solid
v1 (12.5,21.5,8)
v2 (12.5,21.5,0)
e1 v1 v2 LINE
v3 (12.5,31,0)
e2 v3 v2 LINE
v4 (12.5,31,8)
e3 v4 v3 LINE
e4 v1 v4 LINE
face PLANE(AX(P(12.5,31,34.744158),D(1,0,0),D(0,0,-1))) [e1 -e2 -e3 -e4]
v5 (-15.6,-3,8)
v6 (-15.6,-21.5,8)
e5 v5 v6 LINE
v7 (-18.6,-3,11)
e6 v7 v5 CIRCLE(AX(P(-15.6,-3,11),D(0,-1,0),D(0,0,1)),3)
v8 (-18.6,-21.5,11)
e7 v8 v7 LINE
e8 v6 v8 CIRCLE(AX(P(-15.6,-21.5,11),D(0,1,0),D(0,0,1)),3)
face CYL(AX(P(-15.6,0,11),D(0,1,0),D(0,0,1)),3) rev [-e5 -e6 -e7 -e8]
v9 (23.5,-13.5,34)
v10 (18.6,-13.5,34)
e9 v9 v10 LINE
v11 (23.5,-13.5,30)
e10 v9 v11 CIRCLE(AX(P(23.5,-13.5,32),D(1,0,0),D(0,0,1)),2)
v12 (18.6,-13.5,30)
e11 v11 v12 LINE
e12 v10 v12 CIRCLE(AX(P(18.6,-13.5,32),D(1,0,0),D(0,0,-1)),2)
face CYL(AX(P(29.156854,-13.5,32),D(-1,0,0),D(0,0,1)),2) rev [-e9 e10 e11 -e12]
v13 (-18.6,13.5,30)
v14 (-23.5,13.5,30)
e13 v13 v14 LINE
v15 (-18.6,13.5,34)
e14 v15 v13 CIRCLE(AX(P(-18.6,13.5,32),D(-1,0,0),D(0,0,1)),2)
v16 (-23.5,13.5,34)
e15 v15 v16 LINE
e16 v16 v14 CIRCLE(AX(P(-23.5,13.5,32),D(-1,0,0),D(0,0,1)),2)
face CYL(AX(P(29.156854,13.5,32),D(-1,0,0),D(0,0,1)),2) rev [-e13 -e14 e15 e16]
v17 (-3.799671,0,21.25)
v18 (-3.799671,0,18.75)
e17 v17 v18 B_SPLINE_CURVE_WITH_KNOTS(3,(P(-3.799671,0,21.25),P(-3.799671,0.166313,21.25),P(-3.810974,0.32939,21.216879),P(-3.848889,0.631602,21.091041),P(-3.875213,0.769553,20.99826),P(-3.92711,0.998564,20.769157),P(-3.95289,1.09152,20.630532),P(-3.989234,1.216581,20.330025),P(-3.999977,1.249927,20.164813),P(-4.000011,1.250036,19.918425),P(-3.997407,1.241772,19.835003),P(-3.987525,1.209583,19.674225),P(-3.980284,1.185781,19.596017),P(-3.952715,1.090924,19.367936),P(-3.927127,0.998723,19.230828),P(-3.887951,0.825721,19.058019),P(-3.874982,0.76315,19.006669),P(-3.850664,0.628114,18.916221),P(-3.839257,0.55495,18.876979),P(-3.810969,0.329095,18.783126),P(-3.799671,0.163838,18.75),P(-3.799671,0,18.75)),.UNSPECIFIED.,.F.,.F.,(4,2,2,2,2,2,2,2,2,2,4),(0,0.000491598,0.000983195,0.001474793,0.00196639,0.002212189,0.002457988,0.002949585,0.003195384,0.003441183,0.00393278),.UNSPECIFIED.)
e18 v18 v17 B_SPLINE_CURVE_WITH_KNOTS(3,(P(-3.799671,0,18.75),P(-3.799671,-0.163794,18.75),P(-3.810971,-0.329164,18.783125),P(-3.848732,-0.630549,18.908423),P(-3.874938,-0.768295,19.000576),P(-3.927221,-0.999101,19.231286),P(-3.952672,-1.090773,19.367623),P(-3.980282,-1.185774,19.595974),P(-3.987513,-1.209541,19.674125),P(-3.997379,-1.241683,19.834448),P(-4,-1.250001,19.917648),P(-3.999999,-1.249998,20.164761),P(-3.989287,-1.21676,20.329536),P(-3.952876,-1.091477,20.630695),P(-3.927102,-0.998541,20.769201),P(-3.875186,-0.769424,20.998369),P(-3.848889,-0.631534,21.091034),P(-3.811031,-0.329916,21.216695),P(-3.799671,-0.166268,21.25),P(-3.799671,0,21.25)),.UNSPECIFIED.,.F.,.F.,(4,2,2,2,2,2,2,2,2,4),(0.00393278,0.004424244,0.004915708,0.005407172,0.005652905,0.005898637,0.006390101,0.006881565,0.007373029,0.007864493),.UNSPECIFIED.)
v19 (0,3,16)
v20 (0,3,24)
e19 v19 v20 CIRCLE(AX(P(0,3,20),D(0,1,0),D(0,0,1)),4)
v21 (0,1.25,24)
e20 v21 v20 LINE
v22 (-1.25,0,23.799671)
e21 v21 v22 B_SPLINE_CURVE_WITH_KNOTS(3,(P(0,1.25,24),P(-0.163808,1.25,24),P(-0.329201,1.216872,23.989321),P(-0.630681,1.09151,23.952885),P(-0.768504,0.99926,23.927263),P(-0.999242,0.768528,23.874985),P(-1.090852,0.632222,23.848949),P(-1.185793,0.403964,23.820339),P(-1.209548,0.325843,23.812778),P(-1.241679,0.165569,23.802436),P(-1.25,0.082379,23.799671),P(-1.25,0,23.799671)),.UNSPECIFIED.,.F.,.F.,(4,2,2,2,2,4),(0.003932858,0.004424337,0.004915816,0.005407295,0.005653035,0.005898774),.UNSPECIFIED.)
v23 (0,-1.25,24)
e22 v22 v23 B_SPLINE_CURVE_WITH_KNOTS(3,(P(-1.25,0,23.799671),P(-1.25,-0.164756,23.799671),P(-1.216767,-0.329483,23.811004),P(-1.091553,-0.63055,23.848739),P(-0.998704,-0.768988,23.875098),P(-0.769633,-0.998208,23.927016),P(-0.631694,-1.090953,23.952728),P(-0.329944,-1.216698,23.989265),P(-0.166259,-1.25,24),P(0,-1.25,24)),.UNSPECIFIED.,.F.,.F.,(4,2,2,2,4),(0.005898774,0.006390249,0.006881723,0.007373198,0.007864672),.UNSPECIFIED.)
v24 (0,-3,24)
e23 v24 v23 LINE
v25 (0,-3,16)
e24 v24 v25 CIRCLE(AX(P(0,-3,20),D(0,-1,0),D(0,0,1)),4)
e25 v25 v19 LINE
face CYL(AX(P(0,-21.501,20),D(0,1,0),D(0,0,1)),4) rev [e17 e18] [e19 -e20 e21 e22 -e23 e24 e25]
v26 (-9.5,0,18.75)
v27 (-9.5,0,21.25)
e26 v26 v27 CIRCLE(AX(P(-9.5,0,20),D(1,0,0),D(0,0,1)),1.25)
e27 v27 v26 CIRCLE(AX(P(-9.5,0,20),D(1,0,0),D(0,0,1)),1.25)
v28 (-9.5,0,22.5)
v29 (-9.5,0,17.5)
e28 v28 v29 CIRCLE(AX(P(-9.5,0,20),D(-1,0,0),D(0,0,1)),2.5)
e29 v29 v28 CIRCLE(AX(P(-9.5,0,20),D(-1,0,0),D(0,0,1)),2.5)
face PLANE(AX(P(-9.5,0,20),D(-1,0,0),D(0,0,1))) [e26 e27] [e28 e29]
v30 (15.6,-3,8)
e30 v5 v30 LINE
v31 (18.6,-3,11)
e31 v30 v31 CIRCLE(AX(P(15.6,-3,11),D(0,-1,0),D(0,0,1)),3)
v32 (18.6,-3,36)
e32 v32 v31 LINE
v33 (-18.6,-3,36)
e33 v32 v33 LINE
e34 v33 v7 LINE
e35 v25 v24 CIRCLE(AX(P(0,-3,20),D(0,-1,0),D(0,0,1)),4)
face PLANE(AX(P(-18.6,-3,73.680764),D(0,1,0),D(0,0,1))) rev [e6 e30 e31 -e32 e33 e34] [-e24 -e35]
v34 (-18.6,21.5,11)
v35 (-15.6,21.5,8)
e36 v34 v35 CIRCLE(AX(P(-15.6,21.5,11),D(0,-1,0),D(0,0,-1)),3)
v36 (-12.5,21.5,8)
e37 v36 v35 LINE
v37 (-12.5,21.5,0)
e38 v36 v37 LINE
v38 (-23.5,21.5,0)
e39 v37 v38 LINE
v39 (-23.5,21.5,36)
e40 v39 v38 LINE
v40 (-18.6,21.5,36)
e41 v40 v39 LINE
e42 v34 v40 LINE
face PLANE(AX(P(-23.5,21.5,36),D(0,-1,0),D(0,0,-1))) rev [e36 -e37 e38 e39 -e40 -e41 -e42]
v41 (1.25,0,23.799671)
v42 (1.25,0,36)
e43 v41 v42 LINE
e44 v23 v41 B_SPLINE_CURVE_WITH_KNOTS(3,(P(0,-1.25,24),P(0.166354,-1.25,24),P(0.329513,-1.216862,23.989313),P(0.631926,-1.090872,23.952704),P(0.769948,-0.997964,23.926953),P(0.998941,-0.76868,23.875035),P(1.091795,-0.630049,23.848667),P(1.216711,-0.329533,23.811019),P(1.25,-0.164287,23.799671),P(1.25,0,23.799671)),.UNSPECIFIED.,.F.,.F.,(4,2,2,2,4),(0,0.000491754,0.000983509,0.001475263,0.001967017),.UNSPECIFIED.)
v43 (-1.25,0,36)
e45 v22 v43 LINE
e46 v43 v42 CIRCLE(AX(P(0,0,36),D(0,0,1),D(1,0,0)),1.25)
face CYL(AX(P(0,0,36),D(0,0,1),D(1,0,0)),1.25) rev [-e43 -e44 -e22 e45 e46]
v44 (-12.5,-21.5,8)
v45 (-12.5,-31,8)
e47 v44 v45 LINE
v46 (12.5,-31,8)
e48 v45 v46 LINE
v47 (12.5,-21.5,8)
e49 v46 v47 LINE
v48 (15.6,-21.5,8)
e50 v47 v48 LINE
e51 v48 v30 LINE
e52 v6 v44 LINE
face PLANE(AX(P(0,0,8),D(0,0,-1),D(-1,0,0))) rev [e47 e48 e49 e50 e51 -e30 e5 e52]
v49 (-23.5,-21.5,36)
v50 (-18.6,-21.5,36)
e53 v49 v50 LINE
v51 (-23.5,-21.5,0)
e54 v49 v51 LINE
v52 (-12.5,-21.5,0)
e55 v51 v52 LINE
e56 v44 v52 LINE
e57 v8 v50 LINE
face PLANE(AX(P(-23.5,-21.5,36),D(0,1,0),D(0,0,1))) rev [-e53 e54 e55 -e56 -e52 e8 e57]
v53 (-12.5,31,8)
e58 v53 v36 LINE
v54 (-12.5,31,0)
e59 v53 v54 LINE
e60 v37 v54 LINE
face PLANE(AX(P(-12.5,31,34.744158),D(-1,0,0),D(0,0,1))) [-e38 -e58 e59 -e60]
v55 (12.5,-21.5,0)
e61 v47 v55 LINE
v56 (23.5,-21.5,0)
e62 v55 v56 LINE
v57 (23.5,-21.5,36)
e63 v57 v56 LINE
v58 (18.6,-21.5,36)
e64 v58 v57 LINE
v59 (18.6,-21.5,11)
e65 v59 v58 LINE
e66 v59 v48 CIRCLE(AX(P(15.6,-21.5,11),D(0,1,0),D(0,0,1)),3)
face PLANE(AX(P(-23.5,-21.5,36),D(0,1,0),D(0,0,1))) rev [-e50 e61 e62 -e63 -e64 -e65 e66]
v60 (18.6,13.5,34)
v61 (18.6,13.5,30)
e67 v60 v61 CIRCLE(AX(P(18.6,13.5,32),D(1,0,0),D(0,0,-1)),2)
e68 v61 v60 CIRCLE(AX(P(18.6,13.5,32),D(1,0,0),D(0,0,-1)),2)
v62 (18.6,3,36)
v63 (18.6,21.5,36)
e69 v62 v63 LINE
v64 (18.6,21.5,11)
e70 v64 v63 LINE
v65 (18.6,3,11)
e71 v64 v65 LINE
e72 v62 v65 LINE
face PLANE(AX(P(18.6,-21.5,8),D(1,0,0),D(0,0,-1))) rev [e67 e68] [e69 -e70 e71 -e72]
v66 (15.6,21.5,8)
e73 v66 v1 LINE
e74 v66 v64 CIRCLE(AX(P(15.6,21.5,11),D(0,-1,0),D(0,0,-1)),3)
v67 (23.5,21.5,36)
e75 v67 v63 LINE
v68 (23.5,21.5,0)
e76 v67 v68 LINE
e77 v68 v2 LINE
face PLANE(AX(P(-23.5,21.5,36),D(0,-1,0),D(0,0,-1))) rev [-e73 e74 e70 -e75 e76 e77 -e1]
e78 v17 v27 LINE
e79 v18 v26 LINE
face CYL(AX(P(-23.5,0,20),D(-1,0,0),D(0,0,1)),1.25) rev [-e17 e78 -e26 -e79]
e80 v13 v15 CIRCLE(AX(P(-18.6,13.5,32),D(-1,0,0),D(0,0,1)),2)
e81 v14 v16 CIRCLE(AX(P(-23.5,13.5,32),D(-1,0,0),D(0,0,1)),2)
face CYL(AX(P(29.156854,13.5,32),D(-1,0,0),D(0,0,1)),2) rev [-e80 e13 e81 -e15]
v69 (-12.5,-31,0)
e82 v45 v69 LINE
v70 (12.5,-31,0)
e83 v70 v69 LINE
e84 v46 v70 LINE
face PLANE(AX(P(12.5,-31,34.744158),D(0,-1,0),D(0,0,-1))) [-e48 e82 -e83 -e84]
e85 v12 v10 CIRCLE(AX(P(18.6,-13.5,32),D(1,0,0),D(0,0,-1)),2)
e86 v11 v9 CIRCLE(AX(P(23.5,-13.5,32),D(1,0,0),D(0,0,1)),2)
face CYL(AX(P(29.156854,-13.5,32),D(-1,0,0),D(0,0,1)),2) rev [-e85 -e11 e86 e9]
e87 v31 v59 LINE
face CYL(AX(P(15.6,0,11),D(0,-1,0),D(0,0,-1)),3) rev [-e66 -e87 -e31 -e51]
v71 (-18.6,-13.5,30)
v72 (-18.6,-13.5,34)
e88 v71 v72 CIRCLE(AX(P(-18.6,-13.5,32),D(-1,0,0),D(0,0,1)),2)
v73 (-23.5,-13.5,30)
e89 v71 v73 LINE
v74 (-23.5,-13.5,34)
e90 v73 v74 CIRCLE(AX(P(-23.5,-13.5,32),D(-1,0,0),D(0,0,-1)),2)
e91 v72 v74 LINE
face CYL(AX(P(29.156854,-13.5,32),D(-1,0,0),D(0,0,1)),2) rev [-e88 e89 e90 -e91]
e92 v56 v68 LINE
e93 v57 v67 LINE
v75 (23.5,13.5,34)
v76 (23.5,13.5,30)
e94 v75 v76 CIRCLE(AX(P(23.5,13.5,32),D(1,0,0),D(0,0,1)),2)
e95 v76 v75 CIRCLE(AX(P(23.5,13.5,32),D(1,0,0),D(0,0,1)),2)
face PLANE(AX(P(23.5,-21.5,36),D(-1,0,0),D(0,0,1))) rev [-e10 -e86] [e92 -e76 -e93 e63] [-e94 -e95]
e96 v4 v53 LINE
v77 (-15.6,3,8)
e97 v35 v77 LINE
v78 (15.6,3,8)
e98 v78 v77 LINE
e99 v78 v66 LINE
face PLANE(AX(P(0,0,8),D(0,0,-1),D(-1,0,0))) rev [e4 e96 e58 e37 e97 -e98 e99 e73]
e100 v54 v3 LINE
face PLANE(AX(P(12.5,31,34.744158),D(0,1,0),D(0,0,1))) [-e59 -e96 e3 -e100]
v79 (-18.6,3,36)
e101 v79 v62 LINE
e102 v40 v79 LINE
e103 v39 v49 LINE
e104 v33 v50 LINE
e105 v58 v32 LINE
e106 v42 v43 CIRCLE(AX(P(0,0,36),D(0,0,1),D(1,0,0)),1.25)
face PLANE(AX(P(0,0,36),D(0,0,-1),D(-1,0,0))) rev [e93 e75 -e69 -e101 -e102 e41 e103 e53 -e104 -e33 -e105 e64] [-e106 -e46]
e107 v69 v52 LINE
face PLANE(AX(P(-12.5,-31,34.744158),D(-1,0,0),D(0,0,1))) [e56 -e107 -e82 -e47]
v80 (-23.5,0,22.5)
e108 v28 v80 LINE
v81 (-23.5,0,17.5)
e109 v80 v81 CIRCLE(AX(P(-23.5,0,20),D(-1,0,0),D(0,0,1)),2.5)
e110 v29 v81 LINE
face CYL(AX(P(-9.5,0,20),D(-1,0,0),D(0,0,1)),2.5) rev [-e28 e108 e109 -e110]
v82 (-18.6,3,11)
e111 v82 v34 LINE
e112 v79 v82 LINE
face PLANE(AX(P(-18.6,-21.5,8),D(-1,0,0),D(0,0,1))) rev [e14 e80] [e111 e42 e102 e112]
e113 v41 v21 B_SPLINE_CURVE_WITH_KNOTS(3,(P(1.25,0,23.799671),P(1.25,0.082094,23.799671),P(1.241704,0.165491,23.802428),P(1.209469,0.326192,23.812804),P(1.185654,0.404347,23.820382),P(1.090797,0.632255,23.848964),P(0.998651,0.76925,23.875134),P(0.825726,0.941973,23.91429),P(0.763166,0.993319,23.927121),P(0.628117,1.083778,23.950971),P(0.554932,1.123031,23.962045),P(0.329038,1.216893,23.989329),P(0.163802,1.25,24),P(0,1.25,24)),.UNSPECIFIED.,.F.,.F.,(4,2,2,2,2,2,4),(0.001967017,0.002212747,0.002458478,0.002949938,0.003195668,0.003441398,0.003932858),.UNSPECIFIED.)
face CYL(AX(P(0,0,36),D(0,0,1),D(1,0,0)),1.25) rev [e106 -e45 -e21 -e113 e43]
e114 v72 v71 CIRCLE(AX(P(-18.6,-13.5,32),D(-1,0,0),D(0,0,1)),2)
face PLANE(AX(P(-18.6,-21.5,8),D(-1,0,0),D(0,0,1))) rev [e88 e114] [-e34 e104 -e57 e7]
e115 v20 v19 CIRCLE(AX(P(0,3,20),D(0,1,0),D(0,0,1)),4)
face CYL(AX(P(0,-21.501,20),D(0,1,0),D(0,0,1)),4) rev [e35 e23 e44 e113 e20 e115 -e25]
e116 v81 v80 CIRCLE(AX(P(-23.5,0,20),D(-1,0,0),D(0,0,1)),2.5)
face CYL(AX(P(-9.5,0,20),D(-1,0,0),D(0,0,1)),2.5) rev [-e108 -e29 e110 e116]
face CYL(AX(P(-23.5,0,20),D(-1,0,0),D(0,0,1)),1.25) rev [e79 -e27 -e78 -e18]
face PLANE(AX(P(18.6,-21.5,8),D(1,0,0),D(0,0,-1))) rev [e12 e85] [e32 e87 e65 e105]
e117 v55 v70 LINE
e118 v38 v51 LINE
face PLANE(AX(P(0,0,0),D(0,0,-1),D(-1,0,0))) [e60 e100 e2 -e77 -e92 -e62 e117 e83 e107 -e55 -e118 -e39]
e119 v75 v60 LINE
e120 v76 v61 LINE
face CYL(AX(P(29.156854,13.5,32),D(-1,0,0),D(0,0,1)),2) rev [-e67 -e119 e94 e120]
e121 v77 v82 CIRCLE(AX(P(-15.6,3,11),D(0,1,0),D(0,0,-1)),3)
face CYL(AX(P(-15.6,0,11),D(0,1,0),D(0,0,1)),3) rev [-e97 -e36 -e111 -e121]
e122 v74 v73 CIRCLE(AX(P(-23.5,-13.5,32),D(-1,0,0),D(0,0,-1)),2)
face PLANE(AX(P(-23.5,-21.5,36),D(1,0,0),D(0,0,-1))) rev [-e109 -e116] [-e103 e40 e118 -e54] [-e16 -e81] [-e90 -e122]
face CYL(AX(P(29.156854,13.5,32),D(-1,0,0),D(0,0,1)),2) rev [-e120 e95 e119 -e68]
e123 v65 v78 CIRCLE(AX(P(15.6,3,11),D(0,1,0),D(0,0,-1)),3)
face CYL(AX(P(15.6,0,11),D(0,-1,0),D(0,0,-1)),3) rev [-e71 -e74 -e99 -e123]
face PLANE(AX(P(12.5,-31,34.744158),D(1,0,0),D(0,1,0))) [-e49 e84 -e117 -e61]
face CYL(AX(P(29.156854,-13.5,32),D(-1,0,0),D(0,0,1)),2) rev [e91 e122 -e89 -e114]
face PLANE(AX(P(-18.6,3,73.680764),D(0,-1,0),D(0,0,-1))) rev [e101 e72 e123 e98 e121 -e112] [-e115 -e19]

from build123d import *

# Parameters (mm, degrees)
SKETCH_1_W              = 47
SKETCH_1_H              = 43
EXTRUDE_1_DEPTH         = 36
SKETCH_2_W              = 37.2
SKETCH_2_H              = 43
CUT_EXTRUDE_1_DEPTH     = 28
CUT_EXTRUDE_2_REACH     = 64.986
SKETCH_3_R              = 2
SKETCH_4_W              = 37.2
SKETCH_4_H              = 6
EXTRUDE_2_DEPTH         = 28
FILLET_1_R              = 3
CUT_EXTRUDE_3_REACH     = 51.482
SKETCH_5_R              = 4
HOLE_WIZARD_M3_1_REACH  = 50.068
HOLE_WIZARD_M3_1_BORE_R = 1.25
HOLE_WIZARD_M3_2_REACH  = 57.419
HOLE_WIZARD_M3_2_BORE_R = 1.25
SKETCH_8_W              = 25
SKETCH_8_H              = 9.5
EXTRUDE_3_DEPTH         = 8
SKETCH_9_R              = 2.5
CUT_EXTRUDE_4_DEPTH     = 14


with BuildPart() as part:
    # 草图1 → 凸台-拉伸1 (new body)
    with BuildSketch(Plane.XY):
        Rectangle(SKETCH_1_W, SKETCH_1_H)
    extrude(amount=EXTRUDE_1_DEPTH)

    # 草图2 → 切除-拉伸1 (cut)
    with BuildSketch(Plane.XY.offset(36)):
        Rectangle(SKETCH_2_W, SKETCH_2_H)
    extrude(amount=-CUT_EXTRUDE_1_DEPTH, mode=Mode.SUBTRACT)

    # 切除-拉伸2: up to this face of the body (flat: up to its plane)
    cut_extrude_2_end = Plane(part.part.faces().sort_by_distance((23.5, 0, 18))[0])
    # 草图3 → 切除-拉伸2 (cut, up to the picked face)
    with BuildSketch(Plane.ZY.offset(23.5), mode=Mode.PRIVATE) as cut_extrude_2_sk1:
        with Locations((32, 13.5)):
            Circle(SKETCH_3_R)
    cut_extrude_2_tool1 = split(extrude(cut_extrude_2_sk1.sketch, amount=-CUT_EXTRUDE_2_REACH, mode=Mode.PRIVATE), bisect_by=cut_extrude_2_end, keep=Keep.BOTH, mode=Mode.PRIVATE)
    # 草图3 → 切除-拉伸2 (cut, up to the picked face)
    with BuildSketch(Plane.ZY.offset(23.5), mode=Mode.PRIVATE) as cut_extrude_2_sk2:
        with Locations((32, -13.5)):
            Circle(SKETCH_3_R)
    cut_extrude_2_tool2 = split(extrude(cut_extrude_2_sk2.sketch, amount=-CUT_EXTRUDE_2_REACH, mode=Mode.PRIVATE), bisect_by=cut_extrude_2_end, keep=Keep.BOTH, mode=Mode.PRIVATE)
    add(cut_extrude_2_tool1.solids().sort_by(Axis((-23.5, 13.5, 32), (1, 0, 0)))[0], mode=Mode.SUBTRACT)
    add(cut_extrude_2_tool2.solids().sort_by(Axis((-23.5, -13.5, 32), (1, 0, 0)))[0], mode=Mode.SUBTRACT)

    # 草图4 → 凸台-拉伸2 (add)
    with BuildSketch(Plane.XY.offset(8)):
        Rectangle(SKETCH_4_W, SKETCH_4_H)
    extrude(amount=EXTRUDE_2_DEPTH)

    # 圆角1
    fillet_1_edges = [part.edges().sort_by_distance(p)[0] for p in [
        (18.6, -12.25, 8),
        (-18.6, 12.25, 8),
        (18.6, 12.25, 8),
        (-18.6, -12.25, 8),
    ]]
    fillet(fillet_1_edges, radius=FILLET_1_R)

    # 草图5 → 切除-拉伸3 (cut, up to next)
    with BuildSketch(Plane(origin=(0, 3, 0), x_dir=(1, 0, 0), z_dir=(0, 1, 0)), mode=Mode.PRIVATE) as cut_extrude_3_sk1:
        with Locations(Location((0, -20, 0), (0, 0, 270))):
            Circle(SKETCH_5_R)
    cut_extrude_3_tool1 = extrude(cut_extrude_3_sk1.sketch, amount=-CUT_EXTRUDE_3_REACH, mode=Mode.PRIVATE) & part.part
    add(cut_extrude_3_tool1.solids().sort_by_distance((0, 3, 20))[0], mode=Mode.SUBTRACT)

    # M3 螺纹孔1 bore (on position points) → M3 螺纹孔1 (cut, up to next)
    with BuildSketch(Plane.XY.offset(36), mode=Mode.PRIVATE) as hole_wizard_m3_1_sk1:
        Circle(HOLE_WIZARD_M3_1_BORE_R)
    hole_wizard_m3_1_tool1 = extrude(hole_wizard_m3_1_sk1.sketch, amount=-HOLE_WIZARD_M3_1_REACH, mode=Mode.PRIVATE) & part.part
    add(hole_wizard_m3_1_tool1.solids().sort_by_distance((0, 0, 36))[0], mode=Mode.SUBTRACT)

    # M3 螺纹孔2 bore (on position points) → M3 螺纹孔2 (cut, up to next)
    with BuildSketch(Plane(origin=(-23.5, 0, 20), x_dir=(0, 0, -1), z_dir=(-1, 0, 0)), mode=Mode.PRIVATE) as hole_wizard_m3_2_sk1:
        Circle(HOLE_WIZARD_M3_2_BORE_R)
    hole_wizard_m3_2_tool1 = extrude(hole_wizard_m3_2_sk1.sketch, amount=-HOLE_WIZARD_M3_2_REACH, mode=Mode.PRIVATE) & part.part
    add(hole_wizard_m3_2_tool1.solids().sort_by_distance((-23.5, 0, 20))[0], mode=Mode.SUBTRACT)

    # 草图8 → 凸台-拉伸3 (add)
    with BuildSketch(Plane(origin=(0, 0, 0), x_dir=(-1, 0, 0), z_dir=(0, 0, -1))):
        with Locations((0, 26.25)):
            Rectangle(SKETCH_8_W, SKETCH_8_H)
        with Locations((0, -26.25)):
            Rectangle(SKETCH_8_W, SKETCH_8_H)
    extrude(amount=-EXTRUDE_3_DEPTH)

    # 草图9 → 切除-拉伸4 (cut)
    with BuildSketch(Plane.ZY.offset(23.5)):
        with Locations((20, 0)):
            Circle(SKETCH_9_R)
    extrude(amount=-CUT_EXTRUDE_4_DEPTH, mode=Mode.SUBTRACT)


solid = part.part
